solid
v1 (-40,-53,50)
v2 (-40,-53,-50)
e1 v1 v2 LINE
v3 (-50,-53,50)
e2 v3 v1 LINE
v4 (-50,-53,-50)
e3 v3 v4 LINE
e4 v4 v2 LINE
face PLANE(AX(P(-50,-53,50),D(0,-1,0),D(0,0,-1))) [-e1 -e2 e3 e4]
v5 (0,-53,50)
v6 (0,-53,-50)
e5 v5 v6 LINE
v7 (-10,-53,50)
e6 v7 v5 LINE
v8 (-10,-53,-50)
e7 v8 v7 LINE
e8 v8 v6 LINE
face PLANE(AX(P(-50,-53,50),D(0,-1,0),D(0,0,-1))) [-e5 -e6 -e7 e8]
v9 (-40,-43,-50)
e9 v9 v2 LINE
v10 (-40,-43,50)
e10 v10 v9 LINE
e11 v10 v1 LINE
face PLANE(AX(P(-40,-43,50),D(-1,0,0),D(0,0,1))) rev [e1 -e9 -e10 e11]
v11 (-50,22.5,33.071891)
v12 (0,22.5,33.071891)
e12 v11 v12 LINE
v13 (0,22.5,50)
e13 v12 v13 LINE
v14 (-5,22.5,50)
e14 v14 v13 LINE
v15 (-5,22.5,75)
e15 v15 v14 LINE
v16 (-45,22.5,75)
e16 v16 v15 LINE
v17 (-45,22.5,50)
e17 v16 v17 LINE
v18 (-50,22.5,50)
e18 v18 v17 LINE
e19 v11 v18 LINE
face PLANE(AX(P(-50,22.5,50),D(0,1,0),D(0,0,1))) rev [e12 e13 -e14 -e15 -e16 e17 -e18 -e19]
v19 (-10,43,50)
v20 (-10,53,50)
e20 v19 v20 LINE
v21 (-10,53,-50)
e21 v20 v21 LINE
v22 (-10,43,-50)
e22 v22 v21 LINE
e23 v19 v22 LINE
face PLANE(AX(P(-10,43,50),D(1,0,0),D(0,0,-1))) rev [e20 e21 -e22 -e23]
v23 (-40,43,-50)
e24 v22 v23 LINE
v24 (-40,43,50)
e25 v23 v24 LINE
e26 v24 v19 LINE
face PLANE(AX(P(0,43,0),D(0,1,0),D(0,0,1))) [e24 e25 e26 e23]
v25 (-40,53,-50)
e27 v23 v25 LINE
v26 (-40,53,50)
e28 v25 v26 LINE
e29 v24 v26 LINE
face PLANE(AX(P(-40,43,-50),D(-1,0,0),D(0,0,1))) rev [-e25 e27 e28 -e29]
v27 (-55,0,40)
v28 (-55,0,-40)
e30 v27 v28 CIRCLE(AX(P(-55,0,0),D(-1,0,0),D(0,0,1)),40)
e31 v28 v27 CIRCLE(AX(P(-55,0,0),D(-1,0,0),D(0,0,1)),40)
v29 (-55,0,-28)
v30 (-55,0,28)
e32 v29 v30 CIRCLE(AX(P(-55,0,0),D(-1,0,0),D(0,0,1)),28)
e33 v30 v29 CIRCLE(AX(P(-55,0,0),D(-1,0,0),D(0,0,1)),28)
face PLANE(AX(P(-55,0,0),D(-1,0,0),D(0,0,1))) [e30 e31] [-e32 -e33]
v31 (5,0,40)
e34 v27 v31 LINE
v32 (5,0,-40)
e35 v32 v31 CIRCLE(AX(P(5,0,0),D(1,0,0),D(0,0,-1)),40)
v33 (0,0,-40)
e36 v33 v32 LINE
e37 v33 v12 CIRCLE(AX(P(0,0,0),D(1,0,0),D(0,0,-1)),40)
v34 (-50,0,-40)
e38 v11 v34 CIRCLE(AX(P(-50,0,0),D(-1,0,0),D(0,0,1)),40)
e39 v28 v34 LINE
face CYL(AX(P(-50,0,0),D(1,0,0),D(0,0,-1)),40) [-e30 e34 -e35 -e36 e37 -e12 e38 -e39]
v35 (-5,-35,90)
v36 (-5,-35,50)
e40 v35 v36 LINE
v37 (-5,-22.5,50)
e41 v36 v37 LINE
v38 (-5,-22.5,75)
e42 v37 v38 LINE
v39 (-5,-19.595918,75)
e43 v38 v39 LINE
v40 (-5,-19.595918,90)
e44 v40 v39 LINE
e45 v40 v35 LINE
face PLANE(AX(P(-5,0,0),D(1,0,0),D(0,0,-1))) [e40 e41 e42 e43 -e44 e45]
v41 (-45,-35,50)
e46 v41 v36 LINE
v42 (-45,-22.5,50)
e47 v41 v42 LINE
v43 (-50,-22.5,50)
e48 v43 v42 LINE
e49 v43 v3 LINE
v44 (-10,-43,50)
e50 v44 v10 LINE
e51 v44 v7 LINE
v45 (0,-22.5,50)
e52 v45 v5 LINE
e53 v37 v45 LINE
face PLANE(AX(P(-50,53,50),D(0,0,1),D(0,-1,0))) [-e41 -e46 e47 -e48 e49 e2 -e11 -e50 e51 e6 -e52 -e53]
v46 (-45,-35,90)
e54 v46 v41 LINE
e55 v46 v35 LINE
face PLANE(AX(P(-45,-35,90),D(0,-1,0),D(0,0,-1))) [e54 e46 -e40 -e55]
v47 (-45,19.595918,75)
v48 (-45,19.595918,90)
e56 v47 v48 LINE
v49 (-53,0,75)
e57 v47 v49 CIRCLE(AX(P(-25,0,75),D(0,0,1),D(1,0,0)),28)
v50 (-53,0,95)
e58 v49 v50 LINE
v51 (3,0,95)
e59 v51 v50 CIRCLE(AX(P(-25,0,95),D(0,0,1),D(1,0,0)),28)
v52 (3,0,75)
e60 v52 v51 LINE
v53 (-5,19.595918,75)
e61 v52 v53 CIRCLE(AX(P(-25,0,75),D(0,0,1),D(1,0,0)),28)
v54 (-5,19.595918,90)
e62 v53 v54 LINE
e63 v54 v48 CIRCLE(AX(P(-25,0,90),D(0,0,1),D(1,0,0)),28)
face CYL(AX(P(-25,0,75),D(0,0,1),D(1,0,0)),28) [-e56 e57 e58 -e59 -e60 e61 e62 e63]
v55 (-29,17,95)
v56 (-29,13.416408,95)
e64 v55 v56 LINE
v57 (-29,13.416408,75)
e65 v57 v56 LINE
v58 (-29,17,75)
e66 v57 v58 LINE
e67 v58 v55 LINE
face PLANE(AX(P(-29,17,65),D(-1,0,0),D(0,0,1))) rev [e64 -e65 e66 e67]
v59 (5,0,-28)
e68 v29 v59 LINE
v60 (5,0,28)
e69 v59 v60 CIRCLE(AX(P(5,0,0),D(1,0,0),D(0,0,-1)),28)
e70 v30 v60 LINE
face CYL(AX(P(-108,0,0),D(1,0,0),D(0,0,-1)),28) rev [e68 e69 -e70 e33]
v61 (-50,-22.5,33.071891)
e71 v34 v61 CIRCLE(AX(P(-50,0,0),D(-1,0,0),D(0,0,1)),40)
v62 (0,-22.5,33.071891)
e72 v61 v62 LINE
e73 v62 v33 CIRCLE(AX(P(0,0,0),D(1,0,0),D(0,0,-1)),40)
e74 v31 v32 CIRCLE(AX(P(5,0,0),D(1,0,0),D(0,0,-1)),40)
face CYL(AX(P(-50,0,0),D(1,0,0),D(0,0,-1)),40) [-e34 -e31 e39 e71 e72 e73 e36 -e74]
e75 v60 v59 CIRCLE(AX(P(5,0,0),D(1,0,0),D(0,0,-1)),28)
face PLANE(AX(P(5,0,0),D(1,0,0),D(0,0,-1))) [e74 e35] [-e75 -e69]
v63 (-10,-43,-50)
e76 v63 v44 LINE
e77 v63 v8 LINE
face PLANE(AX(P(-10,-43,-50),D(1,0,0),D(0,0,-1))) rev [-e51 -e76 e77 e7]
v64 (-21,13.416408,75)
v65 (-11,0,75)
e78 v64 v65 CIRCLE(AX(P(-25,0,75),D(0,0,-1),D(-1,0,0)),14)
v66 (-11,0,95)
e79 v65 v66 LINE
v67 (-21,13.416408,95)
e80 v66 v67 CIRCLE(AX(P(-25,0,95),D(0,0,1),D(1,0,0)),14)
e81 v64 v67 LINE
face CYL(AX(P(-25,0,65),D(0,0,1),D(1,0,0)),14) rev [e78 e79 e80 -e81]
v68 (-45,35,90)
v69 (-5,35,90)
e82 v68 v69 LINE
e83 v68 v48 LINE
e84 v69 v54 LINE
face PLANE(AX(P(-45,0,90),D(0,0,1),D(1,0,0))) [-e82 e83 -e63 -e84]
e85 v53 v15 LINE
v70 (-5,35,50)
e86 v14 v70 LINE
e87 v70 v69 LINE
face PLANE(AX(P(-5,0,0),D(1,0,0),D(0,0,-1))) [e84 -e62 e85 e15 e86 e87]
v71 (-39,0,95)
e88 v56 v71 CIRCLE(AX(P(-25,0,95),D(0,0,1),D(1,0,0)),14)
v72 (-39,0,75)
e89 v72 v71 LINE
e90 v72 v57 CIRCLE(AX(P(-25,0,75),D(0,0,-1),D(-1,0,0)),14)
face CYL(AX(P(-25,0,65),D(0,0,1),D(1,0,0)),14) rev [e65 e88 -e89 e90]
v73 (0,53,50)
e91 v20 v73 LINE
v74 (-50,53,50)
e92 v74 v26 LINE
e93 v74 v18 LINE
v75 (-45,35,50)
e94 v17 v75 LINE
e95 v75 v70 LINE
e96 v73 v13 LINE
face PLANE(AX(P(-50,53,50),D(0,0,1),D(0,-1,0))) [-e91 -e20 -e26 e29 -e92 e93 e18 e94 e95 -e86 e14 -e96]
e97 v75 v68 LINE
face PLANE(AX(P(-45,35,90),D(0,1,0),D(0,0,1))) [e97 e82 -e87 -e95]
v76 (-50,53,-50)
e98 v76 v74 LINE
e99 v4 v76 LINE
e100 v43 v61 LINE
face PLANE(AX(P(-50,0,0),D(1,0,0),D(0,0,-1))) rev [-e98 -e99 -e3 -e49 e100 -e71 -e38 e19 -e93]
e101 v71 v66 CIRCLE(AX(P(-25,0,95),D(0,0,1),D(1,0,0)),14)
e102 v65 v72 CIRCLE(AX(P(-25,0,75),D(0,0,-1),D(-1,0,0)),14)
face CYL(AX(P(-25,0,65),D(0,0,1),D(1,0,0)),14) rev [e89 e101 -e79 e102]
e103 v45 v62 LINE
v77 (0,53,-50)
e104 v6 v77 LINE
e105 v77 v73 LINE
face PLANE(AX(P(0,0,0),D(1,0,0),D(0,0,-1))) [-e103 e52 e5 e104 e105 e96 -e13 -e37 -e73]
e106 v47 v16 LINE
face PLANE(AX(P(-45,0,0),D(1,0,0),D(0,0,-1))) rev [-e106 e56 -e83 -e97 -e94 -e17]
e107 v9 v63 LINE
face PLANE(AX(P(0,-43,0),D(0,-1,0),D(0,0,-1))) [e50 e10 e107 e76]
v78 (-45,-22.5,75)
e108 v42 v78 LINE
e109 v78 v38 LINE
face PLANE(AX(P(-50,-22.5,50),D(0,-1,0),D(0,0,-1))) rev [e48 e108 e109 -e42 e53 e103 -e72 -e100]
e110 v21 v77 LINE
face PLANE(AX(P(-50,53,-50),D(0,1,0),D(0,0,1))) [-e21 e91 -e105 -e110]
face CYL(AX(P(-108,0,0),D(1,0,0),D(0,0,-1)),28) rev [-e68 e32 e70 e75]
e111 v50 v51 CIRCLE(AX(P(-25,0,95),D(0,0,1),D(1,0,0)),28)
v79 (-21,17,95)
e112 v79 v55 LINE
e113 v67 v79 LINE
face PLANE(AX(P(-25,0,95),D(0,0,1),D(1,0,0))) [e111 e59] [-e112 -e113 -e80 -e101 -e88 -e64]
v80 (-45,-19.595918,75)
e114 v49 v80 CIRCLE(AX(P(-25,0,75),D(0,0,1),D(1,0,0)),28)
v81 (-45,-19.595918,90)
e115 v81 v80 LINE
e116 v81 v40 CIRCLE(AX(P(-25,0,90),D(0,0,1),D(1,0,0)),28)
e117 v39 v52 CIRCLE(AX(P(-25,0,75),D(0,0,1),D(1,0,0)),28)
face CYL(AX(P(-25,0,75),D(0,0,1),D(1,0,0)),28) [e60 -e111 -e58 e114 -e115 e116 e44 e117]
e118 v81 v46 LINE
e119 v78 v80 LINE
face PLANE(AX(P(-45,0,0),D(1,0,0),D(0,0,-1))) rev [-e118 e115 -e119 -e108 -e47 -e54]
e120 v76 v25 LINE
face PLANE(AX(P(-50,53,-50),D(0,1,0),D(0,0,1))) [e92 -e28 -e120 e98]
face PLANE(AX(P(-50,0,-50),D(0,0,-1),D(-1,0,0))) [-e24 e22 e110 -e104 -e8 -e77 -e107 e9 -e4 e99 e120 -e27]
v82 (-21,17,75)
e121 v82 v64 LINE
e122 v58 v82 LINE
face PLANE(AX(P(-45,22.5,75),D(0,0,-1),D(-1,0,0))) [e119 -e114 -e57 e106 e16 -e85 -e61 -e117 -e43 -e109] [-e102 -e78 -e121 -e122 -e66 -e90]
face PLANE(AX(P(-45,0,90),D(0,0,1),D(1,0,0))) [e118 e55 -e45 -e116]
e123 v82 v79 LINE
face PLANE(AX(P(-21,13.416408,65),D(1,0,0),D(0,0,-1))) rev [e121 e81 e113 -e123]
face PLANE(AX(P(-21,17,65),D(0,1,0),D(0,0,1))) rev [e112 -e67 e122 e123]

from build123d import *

# Parameters (mm, degrees)
BASE_BLOCK_DEPTH          = 50
BODY_RECESS_CUT_DEPTH     = 50
BEARING_HUB_PROFILE_R     = 40
BEARING_HUB_BOSS_DEPTH    = 50
HUB_START                 = 5
HUB_FLANGE_PROFILE_R      = 40
HUB_FLANGE_BOSS_DEPTH     = 5
MAIN_BORE_PROFILE_R       = 28
MAIN_BORE_CUT_DEPTH       = 113
TOP_SLOT_PROFILE_W        = 30
TOP_SLOT_PROFILE_H        = 100
TOP_SLOT_CUT_DEPTH        = 10
SIDE_ARM_BOSS_DEPTH       = 40
ARM_HOLE_PROFILE_R        = 28
ARM_HOLE_CUT_DEPTH        = 15
SHAFT_HUB_BOSS_DEPTH      = 5
SHAFT_HUB_BOSS_DEPTH_BACK = 15
SHAFT_HUB_PROFILE_R       = 28
KEYED_BORE_CUT_DEPTH      = 30
REAR_RING_PROFILE_R       = 40
REAR_RING_BOSS_DEPTH      = 5
THROUGH_BORE_PROFILE_R    = 28
THROUGH_BORE_CUT_DEPTH    = 194
SECOND_SLOT_PROFILE_W     = 30
SECOND_SLOT_PROFILE_H     = 100
SECOND_SLOT_CUT_DEPTH     = 10


with BuildPart() as part:
    # Base Block Profile → Base Block (new body)
    with BuildSketch(Plane(origin=(0, 0, 0), x_dir=(0, 0, -1), z_dir=(1, 0, 0))):
        Polygon((50, 0), (50, 53), (-50, 53), (-50, -53), (50, -53), align=None)
    extrude(amount=-BASE_BLOCK_DEPTH)

    # Body Recess Profile → Body Recess Cut (cut)
    with BuildSketch(Plane(origin=(0, 0, 0), x_dir=(0, 0, -1), z_dir=(1, 0, 0))):
        with BuildLine():
            Line((-50, 0), (-50, 22.5))
            Line((-50, 22.5), (-33.071891388, 22.5))
            ThreePointArc((-33.071891388, 22.5), (40, 0), (-33.071891388, -22.5))
            Line((-33.071891388, -22.5), (-50, -22.5))
            Line((-50, -22.5), (-50, 0))
        make_face()
    extrude(amount=-BODY_RECESS_CUT_DEPTH, mode=Mode.SUBTRACT)

    # Bearing Hub Profile → Bearing Hub Boss (add)
    with BuildSketch(Plane(origin=(0, 0, 0), x_dir=(0, 0, -1), z_dir=(1, 0, 0))):
        Circle(BEARING_HUB_PROFILE_R)
    extrude(amount=-BEARING_HUB_BOSS_DEPTH)

    # Hub Flange Profile → Hub Flange Boss (add)
    with BuildSketch(Plane(origin=(0, 0, 0), x_dir=(0, 0, -1), z_dir=(1, 0, 0)).offset(HUB_START)):
        Circle(HUB_FLANGE_PROFILE_R)
    extrude(amount=-HUB_FLANGE_BOSS_DEPTH)

    # Main Bore Profile → Main Bore Cut (cut)
    with BuildSketch(Plane(origin=(5, 0, 0), x_dir=(0, 0, -1), z_dir=(1, 0, 0))):
        Circle(MAIN_BORE_PROFILE_R)
    extrude(amount=-MAIN_BORE_CUT_DEPTH, mode=Mode.SUBTRACT)

    # Top Slot Profile → Top Slot Cut (cut)
    with BuildSketch(Plane(origin=(0, 53, 0), x_dir=(1, 0, 0), z_dir=(0, 1, 0))):
        with Locations((-25, 0)):
            Rectangle(TOP_SLOT_PROFILE_W, TOP_SLOT_PROFILE_H)
    extrude(amount=-TOP_SLOT_CUT_DEPTH, mode=Mode.SUBTRACT)

    # Side Arm Profile → Side Arm Boss (add)
    with BuildSketch(Plane(origin=(-5, 0, 0), x_dir=(0, 0, -1), z_dir=(1, 0, 0))):
        Polygon((-90, 0), (-90, 35), (-50, 35), (-50, 22.5), (-75, 22.5), (-75, -22.5), (-50, -22.5), (-50, -35), (-90, -35), align=None)
    extrude(amount=-SIDE_ARM_BOSS_DEPTH)

    # Arm Hole Profile → Arm Hole Cut (cut)
    with BuildSketch(Plane.XY.offset(90)):
        with Locations((-25, 0)):
            Circle(ARM_HOLE_PROFILE_R)
    extrude(amount=-ARM_HOLE_CUT_DEPTH, mode=Mode.SUBTRACT)

    # Shaft Hub Profile → Shaft Hub Boss (add, two sides: drawn at the far end of the back side and taken through both)
    with BuildSketch(Plane.XY.offset(90).offset(-SHAFT_HUB_BOSS_DEPTH_BACK)):
        with Locations((-25, 0)):
            Circle(SHAFT_HUB_PROFILE_R)
    extrude(amount=SHAFT_HUB_BOSS_DEPTH + SHAFT_HUB_BOSS_DEPTH_BACK)

    # Keyed Bore Profile → Keyed Bore Cut (cut)
    with BuildSketch(Plane.XY.offset(95)):
        with BuildLine():
            Line((-21, 13.416407865), (-21, 17))
            Line((-21, 17), (-29, 17))
            Line((-29, 17), (-29, 13.416407865))
            ThreePointArc((-29, 13.416407865), (-25, -14), (-21, 13.416407865))
        make_face()
    extrude(amount=-KEYED_BORE_CUT_DEPTH, mode=Mode.SUBTRACT)

    # Rear Ring Profile → Rear Ring Boss (add)
    with BuildSketch(Plane.ZY.offset(50)):
        with Locations(Location((0, 0, 0), (0, 0, 180))):
            Circle(REAR_RING_PROFILE_R)
    extrude(amount=REAR_RING_BOSS_DEPTH)

    # Through Bore Profile → Through Bore Cut (cut)
    with BuildSketch(Plane(origin=(5, 0, 0), x_dir=(0, 0, -1), z_dir=(1, 0, 0))):
        Circle(THROUGH_BORE_PROFILE_R)
    extrude(amount=-THROUGH_BORE_CUT_DEPTH, mode=Mode.SUBTRACT)

    # Second Slot Profile → Second Slot Cut (cut)
    with BuildSketch(Plane.XZ.offset(53)):
        with Locations((-25, 0)):
            Rectangle(SECOND_SLOT_PROFILE_W, SECOND_SLOT_PROFILE_H)
    extrude(amount=-SECOND_SLOT_CUT_DEPTH, mode=Mode.SUBTRACT)


solid = part.part
